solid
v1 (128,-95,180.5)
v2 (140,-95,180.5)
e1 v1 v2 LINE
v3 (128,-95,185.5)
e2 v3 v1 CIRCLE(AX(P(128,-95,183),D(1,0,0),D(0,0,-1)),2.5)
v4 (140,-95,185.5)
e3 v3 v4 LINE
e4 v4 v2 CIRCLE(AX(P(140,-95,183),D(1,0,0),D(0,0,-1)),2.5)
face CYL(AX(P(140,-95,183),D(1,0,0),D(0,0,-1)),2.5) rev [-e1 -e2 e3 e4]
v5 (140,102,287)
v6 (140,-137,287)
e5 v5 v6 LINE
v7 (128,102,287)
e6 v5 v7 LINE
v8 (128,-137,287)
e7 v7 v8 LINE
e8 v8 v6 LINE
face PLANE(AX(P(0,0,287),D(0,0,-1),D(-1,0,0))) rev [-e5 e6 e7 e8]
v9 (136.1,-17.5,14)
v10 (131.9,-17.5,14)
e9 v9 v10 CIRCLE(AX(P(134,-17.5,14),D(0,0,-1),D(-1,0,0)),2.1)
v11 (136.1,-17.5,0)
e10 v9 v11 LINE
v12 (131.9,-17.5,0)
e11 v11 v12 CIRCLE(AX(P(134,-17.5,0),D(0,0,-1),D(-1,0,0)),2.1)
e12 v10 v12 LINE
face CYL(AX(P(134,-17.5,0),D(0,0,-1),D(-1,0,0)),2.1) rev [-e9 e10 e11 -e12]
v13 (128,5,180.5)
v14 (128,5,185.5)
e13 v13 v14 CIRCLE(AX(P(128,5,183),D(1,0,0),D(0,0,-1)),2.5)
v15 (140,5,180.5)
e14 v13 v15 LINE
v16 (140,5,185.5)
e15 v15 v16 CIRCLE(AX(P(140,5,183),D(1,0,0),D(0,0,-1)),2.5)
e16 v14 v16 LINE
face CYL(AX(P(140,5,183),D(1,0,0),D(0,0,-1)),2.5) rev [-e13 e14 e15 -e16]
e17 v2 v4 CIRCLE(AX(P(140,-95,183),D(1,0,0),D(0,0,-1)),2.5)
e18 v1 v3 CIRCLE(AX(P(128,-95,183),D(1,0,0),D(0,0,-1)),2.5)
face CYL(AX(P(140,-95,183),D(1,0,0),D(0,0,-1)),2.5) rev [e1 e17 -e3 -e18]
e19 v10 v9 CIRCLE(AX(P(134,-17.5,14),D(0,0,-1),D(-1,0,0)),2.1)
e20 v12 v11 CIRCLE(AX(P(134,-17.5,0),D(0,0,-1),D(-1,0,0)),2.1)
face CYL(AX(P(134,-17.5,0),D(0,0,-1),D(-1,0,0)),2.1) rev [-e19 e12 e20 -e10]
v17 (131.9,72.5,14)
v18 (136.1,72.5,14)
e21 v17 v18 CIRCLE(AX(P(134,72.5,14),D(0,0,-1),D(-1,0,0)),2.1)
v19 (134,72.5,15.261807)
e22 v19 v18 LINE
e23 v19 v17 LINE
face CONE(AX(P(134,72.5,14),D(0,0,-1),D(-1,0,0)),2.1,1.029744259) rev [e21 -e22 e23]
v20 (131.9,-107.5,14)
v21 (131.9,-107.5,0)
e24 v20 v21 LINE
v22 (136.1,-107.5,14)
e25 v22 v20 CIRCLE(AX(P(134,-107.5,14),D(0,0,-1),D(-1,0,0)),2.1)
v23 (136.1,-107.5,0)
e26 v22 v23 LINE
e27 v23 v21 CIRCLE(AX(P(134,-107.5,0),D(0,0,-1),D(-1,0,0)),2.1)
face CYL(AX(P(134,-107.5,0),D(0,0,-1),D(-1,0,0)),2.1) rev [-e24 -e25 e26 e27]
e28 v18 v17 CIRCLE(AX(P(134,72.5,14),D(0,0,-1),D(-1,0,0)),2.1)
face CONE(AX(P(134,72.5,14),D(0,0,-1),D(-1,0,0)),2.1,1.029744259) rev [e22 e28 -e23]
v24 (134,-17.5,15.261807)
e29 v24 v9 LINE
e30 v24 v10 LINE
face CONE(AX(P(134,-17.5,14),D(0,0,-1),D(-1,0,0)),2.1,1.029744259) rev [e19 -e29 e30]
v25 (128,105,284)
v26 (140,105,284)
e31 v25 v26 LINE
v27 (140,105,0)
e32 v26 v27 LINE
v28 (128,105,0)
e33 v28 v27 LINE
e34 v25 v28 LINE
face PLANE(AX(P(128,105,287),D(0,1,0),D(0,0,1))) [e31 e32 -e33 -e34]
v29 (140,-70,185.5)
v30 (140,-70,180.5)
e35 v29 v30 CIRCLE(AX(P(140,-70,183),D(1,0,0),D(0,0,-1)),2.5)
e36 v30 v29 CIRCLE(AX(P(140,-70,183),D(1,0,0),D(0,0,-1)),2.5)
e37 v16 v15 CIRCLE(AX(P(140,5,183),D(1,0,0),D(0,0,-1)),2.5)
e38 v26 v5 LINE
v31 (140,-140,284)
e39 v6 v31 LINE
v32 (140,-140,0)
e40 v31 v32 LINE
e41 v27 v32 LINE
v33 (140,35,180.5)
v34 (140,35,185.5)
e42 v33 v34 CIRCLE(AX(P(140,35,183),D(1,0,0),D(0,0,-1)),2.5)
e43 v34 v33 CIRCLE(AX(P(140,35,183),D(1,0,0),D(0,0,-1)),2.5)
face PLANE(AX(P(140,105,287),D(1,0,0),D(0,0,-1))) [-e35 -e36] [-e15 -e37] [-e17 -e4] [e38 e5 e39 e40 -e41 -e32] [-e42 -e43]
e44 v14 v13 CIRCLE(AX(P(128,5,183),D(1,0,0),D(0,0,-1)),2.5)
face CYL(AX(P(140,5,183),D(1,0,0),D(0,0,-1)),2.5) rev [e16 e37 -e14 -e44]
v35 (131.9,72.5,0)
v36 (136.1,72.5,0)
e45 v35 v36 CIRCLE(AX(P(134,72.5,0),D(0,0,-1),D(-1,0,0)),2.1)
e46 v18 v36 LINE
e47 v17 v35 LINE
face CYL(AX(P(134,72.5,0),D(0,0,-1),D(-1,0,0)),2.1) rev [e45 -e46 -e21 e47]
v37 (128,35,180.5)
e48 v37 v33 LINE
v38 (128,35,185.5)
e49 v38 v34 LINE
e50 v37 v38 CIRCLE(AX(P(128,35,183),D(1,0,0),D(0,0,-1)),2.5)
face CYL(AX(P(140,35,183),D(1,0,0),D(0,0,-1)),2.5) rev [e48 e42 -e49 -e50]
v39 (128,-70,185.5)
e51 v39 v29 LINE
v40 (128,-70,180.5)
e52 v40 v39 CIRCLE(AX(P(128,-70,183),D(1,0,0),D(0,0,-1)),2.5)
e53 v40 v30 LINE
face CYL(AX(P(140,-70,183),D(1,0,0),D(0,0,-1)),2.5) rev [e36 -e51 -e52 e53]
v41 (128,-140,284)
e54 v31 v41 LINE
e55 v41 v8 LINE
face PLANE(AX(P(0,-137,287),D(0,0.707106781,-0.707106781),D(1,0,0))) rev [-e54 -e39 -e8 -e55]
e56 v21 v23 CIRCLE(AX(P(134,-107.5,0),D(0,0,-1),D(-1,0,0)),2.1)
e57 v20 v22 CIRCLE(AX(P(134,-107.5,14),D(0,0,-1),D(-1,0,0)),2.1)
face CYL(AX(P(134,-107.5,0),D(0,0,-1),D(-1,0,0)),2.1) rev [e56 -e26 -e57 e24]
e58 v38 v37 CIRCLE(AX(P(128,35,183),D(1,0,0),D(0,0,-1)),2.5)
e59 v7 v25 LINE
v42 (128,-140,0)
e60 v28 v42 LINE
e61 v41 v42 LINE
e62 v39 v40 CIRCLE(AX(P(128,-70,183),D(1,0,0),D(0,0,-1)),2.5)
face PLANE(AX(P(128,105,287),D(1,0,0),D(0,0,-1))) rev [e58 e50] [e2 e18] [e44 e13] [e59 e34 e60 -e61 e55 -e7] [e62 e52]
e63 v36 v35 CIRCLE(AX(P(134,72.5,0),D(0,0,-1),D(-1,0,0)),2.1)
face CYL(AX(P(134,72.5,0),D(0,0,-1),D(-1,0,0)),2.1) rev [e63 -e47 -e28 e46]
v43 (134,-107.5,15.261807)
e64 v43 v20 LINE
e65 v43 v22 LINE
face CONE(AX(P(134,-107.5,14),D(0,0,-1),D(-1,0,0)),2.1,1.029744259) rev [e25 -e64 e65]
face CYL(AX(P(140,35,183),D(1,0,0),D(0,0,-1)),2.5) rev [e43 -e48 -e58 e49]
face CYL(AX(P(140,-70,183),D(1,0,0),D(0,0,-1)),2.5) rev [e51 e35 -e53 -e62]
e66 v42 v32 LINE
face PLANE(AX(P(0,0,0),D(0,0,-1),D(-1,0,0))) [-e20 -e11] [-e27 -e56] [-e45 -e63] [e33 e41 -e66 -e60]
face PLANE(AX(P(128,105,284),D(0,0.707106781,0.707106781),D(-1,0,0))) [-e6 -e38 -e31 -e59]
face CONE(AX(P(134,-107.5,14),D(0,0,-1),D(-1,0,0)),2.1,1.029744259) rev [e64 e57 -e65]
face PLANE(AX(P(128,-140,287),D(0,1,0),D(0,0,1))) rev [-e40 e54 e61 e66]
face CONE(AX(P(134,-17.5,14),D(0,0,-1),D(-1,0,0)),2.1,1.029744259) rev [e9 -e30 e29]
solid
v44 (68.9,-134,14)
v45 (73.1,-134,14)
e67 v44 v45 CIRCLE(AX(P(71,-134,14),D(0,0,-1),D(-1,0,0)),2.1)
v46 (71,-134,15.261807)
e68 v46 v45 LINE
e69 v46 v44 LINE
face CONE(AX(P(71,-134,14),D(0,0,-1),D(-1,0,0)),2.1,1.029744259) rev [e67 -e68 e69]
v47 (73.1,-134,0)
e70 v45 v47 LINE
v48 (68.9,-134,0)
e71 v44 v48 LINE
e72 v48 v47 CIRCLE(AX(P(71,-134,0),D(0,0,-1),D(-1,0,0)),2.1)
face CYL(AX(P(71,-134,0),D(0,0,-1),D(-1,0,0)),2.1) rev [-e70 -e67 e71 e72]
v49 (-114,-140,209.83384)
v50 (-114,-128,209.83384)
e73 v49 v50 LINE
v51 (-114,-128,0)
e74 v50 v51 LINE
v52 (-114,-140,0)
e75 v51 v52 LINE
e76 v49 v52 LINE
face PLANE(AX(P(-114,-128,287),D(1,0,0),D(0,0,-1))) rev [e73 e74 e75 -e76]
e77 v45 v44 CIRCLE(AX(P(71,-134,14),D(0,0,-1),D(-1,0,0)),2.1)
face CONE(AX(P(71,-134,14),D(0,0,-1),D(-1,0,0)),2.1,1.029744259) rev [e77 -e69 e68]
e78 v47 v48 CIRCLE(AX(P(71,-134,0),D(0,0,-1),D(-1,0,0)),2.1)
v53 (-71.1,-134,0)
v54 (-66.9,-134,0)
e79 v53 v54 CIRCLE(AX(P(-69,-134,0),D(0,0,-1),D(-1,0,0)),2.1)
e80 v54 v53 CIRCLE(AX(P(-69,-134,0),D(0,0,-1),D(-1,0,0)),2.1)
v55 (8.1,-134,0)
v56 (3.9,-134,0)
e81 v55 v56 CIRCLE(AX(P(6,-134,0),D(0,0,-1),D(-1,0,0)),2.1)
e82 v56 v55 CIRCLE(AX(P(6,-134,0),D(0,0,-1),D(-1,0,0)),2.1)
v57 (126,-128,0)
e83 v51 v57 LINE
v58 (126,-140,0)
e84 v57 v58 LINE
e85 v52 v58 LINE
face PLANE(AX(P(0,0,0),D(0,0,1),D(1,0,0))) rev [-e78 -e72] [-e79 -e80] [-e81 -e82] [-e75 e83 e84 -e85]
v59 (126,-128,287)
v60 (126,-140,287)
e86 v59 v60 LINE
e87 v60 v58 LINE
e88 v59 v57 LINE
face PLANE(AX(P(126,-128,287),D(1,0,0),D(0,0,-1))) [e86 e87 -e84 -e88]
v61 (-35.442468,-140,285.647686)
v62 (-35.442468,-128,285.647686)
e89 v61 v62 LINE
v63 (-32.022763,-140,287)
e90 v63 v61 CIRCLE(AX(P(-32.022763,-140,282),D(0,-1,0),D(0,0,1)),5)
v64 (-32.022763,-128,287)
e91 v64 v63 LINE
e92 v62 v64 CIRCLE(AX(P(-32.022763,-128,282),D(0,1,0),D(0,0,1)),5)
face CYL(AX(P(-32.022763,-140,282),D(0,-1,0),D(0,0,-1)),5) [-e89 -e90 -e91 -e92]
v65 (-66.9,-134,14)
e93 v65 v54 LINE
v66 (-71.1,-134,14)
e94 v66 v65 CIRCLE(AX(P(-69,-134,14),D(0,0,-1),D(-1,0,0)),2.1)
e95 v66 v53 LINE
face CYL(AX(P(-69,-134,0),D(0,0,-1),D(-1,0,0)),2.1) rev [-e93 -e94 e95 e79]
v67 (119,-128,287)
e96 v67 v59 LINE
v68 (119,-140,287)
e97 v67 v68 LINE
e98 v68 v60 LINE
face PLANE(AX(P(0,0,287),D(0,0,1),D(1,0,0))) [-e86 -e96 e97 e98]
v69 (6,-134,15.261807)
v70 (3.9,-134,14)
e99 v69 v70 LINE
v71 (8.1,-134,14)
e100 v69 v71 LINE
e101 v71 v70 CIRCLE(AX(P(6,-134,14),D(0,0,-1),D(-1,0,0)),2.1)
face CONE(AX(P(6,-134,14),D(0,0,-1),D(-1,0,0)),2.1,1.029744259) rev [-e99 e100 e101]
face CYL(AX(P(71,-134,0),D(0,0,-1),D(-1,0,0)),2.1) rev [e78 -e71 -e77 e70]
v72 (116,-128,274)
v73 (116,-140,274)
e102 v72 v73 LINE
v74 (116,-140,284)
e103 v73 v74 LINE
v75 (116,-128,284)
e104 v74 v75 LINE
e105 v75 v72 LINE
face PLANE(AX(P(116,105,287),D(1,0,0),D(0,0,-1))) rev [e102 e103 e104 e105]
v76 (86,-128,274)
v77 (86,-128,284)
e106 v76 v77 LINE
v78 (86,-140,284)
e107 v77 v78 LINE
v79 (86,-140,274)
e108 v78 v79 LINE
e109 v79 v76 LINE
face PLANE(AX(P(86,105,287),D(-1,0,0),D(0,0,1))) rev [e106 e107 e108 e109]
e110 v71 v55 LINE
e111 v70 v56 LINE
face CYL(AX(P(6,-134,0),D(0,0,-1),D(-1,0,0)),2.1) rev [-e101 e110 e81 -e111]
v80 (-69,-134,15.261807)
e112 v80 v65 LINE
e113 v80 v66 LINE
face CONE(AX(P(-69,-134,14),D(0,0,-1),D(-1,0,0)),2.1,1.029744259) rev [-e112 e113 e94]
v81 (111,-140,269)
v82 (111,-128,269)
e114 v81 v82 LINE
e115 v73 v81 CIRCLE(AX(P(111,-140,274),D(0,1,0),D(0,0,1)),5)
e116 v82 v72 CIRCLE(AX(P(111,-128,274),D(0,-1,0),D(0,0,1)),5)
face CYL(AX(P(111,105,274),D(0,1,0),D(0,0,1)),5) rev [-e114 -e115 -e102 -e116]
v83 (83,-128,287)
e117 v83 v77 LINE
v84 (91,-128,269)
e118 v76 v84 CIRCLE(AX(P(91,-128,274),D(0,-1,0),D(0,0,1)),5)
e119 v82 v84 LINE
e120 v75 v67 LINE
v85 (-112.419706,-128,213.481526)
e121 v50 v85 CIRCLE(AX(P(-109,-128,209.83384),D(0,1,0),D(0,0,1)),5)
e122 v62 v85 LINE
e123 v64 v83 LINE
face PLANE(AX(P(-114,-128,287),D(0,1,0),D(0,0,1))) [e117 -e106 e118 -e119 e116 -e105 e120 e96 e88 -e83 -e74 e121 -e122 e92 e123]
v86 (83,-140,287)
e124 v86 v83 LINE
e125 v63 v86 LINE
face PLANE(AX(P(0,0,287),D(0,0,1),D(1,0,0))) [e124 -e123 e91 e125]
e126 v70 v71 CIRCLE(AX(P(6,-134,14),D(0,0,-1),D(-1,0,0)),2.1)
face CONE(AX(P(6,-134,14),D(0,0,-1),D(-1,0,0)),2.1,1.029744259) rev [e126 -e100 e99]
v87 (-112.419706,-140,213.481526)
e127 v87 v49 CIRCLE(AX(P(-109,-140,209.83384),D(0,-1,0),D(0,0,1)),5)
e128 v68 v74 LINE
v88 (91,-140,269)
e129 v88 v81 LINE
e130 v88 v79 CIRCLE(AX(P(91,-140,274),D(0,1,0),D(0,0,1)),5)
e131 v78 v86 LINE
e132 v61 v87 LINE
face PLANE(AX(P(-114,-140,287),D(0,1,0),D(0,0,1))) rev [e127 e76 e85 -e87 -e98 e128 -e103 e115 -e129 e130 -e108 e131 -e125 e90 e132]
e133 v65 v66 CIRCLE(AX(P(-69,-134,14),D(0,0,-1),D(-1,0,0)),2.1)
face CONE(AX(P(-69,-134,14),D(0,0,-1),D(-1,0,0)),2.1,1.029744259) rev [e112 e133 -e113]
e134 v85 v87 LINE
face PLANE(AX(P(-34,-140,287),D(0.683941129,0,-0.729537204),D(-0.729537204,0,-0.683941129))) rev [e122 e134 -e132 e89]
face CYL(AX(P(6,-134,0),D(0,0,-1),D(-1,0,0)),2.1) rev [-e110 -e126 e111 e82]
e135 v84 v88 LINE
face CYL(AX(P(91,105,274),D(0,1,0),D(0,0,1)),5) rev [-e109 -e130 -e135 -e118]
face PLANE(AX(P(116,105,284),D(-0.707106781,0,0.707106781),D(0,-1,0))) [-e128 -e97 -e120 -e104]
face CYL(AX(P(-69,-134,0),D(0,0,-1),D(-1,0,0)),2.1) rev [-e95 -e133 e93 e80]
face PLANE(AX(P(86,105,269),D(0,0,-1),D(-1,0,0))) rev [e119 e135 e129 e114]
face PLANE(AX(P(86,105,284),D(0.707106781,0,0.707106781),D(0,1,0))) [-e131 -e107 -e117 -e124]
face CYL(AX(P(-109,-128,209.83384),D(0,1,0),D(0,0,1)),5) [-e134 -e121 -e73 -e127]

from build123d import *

# Parameters (mm, degrees)
SKETCH1_W                  = 12
SKETCH1_H                  = 245
BOSS_EXTRUDE1_DEPTH        = 287
SKETCH1_W_2                = 240
SKETCH1_H_2                = 12
BOSS_EXTRUDE1_2_DEPTH      = 287
SKETCH3_W                  = 30
SKETCH3_H                  = 18
CUT_EXTRUDE1_DEPTH         = 403.484782321
M5_TAPPED_HOLE1_AT_2_COUNT = 2
M5_TAPPED_HOLE1_AT_2_PITCH = 90
M5_TAPPED_HOLE1_AT_3_COUNT = 2
M5_TAPPED_HOLE1_AT_3_PITCH = 180
M5_TAPPED_HOLE1_AT_4_COUNT = 2
M5_TAPPED_HOLE1_AT_4_PITCH = 215.896387186
M5_TAPPED_HOLE1_AT_5_COUNT = 2
M5_TAPPED_HOLE1_AT_5_PITCH = 242.953184791
M5_TAPPED_HOLE1_AT_6_COUNT = 2
M5_TAPPED_HOLE1_AT_6_PITCH = 289.570803086
CHAMFER1_SIZE              = 3
FILLET1_R                  = 5
CHAMFER2_SIZE              = 3
M6_TAPPED_HOLE1_AT_2_COUNT = 2
M6_TAPPED_HOLE1_AT_2_PITCH = 130
M6_TAPPED_HOLE2_AT_2_COUNT = 2
M6_TAPPED_HOLE2_AT_2_PITCH = 75
CUT_EXTRUDE3_DEPTH         = 396.29482668
FILLET3_R                  = 5


with BuildPart() as part:
    # Sketch1 → Boss-Extrude1 (new body)
    with BuildSketch(Plane.XY):
        with Locations((134, -17.5)):
            Rectangle(SKETCH1_W, SKETCH1_H)
    extrude(amount=BOSS_EXTRUDE1_DEPTH)

    # Sketch5 → M5 Tapped Hole1 (revolve, cut)
    with BuildSketch(Plane(origin=(134, 72.5, 0), x_dir=(0, 1, 0), z_dir=(1, 0, 0))):
        Polygon((0, 0), (0, 15.2618073), (2.1, 14), (2.1, 0), align=None)
    m5_tapped_hole1 = revolve(axis=Axis((134, 72.5, -6.35), (0, 0, 1)), mode=Mode.SUBTRACT)

    # M5 Tapped Hole1 at 2: M5 Tapped Hole1 ×2
    with Locations(*[(0, -i * M5_TAPPED_HOLE1_AT_2_PITCH, 0) for i in range(1, M5_TAPPED_HOLE1_AT_2_COUNT)]):
        add(m5_tapped_hole1, mode=Mode.SUBTRACT)

    # M5 Tapped Hole1 at 3: M5 Tapped Hole1 ×2
    with Locations(*[(0, -i * M5_TAPPED_HOLE1_AT_3_PITCH, 0) for i in range(1, M5_TAPPED_HOLE1_AT_3_COUNT)]):
        add(m5_tapped_hole1, mode=Mode.SUBTRACT)

    # Chamfer2
    chamfer2_edges = [part.edges().sort_by_distance(p)[0] for p in [
        (134, -140, 287),
        (134, 105, 287),
    ]]
    chamfer(chamfer2_edges, length=CHAMFER2_SIZE)

    # Sketch8 → M6 Tapped Hole1 (revolve, cut)
    with BuildSketch(Plane(origin=(140, 35, 183), x_dir=(0, 0, -1), z_dir=(0, 1, 0))):
        Polygon((0, 0), (0, 18.502151548), (2.5, 17), (2.5, 0), align=None)
    m6_tapped_hole1 = revolve(axis=Axis((146.35, 35, 183), (-1, 0, 0)), mode=Mode.SUBTRACT)

    # M6 Tapped Hole1 at 2: M6 Tapped Hole1 ×2
    with Locations(*[(0, -i * M6_TAPPED_HOLE1_AT_2_PITCH, 0) for i in range(1, M6_TAPPED_HOLE1_AT_2_COUNT)]):
        add(m6_tapped_hole1, mode=Mode.SUBTRACT)

    # Sketch10 → M6 Tapped Hole2 (revolve, cut)
    with BuildSketch(Plane(origin=(140, -70, 183), x_dir=(0, 0, -1), z_dir=(0, 1, 0))):
        Polygon((0, 0), (0, 18.502151548), (2.5, 17), (2.5, 0), align=None)
    m6_tapped_hole2 = revolve(axis=Axis((146.35, -70, 183), (-1, 0, 0)), mode=Mode.SUBTRACT)

    # M6 Tapped Hole2 at 2: M6 Tapped Hole2 ×2
    with Locations(*[(0, i * M6_TAPPED_HOLE2_AT_2_PITCH, 0) for i in range(1, M6_TAPPED_HOLE2_AT_2_COUNT)]):
        add(m6_tapped_hole2, mode=Mode.SUBTRACT)


with BuildPart() as body_2:
    # Sketch1 → Boss-Extrude1 2 (new body)
    with BuildSketch(Plane.XY):
        with Locations((6, -134)):
            Rectangle(SKETCH1_W_2, SKETCH1_H_2)
    extrude(amount=BOSS_EXTRUDE1_2_DEPTH)

    # Sketch3 → Cut-Extrude1 (cut, through all)
    with BuildSketch(Plane.XZ.offset(140)):
        with Locations((101, 278)):
            Rectangle(SKETCH3_W, SKETCH3_H)
    extrude(amount=-CUT_EXTRUDE1_DEPTH, mode=Mode.SUBTRACT)

    # M5 Tapped Hole1 at 4: M5 Tapped Hole1 ×2
    with Locations(*[Vector(-0.2918066430898717, -0.9564773301279128, 0) * (i * M5_TAPPED_HOLE1_AT_4_PITCH) for i in range(1, M5_TAPPED_HOLE1_AT_4_COUNT)]):
        add(m5_tapped_hole1, mode=Mode.SUBTRACT)

    # M5 Tapped Hole1 at 5: M5 Tapped Hole1 ×2
    with Locations(*[Vector(-0.526850471666832, -0.8499579874937565, 0) * (i * M5_TAPPED_HOLE1_AT_5_PITCH) for i in range(1, M5_TAPPED_HOLE1_AT_5_COUNT)]):
        add(m5_tapped_hole1, mode=Mode.SUBTRACT)

    # M5 Tapped Hole1 at 6: M5 Tapped Hole1 ×2
    with Locations(*[Vector(-0.7010375280810152, -0.7131243820134465, 0) * (i * M5_TAPPED_HOLE1_AT_6_PITCH) for i in range(1, M5_TAPPED_HOLE1_AT_6_COUNT)]):
        add(m5_tapped_hole1, mode=Mode.SUBTRACT)

    # Chamfer1
    chamfer1_edges = [body_2.edges().sort_by_distance(p)[0] for p in [
        (116, -134, 287),
        (86, -134, 287),
        (-114, -134, 287),
    ]]
    chamfer(chamfer1_edges, length=CHAMFER1_SIZE)

    # Fillet1
    fillet1_edges = [body_2.edges().sort_by_distance(p)[0] for p in [
        (86, -134, 269),
        (116, -134, 269),
    ]]
    fillet(fillet1_edges, radius=FILLET1_R)

    # Sketch11 → Cut-Extrude3 (cut, through all)
    with BuildSketch(Plane(origin=(0, -128, 0), x_dir=(1, 0, 0), z_dir=(0, 1, 0))):
        Polygon((-34, -287), (-114, -212), (-114, -287), align=None)
    extrude(amount=-CUT_EXTRUDE3_DEPTH, mode=Mode.SUBTRACT)

    # Fillet3
    fillet3_edges = [body_2.edges().sort_by_distance(p)[0] for p in [
        (-34, -134, 287),
        (-114, -134, 212),
    ]]
    fillet(fillet3_edges, radius=FILLET3_R)


solid = Compound([part.part, body_2.part])
